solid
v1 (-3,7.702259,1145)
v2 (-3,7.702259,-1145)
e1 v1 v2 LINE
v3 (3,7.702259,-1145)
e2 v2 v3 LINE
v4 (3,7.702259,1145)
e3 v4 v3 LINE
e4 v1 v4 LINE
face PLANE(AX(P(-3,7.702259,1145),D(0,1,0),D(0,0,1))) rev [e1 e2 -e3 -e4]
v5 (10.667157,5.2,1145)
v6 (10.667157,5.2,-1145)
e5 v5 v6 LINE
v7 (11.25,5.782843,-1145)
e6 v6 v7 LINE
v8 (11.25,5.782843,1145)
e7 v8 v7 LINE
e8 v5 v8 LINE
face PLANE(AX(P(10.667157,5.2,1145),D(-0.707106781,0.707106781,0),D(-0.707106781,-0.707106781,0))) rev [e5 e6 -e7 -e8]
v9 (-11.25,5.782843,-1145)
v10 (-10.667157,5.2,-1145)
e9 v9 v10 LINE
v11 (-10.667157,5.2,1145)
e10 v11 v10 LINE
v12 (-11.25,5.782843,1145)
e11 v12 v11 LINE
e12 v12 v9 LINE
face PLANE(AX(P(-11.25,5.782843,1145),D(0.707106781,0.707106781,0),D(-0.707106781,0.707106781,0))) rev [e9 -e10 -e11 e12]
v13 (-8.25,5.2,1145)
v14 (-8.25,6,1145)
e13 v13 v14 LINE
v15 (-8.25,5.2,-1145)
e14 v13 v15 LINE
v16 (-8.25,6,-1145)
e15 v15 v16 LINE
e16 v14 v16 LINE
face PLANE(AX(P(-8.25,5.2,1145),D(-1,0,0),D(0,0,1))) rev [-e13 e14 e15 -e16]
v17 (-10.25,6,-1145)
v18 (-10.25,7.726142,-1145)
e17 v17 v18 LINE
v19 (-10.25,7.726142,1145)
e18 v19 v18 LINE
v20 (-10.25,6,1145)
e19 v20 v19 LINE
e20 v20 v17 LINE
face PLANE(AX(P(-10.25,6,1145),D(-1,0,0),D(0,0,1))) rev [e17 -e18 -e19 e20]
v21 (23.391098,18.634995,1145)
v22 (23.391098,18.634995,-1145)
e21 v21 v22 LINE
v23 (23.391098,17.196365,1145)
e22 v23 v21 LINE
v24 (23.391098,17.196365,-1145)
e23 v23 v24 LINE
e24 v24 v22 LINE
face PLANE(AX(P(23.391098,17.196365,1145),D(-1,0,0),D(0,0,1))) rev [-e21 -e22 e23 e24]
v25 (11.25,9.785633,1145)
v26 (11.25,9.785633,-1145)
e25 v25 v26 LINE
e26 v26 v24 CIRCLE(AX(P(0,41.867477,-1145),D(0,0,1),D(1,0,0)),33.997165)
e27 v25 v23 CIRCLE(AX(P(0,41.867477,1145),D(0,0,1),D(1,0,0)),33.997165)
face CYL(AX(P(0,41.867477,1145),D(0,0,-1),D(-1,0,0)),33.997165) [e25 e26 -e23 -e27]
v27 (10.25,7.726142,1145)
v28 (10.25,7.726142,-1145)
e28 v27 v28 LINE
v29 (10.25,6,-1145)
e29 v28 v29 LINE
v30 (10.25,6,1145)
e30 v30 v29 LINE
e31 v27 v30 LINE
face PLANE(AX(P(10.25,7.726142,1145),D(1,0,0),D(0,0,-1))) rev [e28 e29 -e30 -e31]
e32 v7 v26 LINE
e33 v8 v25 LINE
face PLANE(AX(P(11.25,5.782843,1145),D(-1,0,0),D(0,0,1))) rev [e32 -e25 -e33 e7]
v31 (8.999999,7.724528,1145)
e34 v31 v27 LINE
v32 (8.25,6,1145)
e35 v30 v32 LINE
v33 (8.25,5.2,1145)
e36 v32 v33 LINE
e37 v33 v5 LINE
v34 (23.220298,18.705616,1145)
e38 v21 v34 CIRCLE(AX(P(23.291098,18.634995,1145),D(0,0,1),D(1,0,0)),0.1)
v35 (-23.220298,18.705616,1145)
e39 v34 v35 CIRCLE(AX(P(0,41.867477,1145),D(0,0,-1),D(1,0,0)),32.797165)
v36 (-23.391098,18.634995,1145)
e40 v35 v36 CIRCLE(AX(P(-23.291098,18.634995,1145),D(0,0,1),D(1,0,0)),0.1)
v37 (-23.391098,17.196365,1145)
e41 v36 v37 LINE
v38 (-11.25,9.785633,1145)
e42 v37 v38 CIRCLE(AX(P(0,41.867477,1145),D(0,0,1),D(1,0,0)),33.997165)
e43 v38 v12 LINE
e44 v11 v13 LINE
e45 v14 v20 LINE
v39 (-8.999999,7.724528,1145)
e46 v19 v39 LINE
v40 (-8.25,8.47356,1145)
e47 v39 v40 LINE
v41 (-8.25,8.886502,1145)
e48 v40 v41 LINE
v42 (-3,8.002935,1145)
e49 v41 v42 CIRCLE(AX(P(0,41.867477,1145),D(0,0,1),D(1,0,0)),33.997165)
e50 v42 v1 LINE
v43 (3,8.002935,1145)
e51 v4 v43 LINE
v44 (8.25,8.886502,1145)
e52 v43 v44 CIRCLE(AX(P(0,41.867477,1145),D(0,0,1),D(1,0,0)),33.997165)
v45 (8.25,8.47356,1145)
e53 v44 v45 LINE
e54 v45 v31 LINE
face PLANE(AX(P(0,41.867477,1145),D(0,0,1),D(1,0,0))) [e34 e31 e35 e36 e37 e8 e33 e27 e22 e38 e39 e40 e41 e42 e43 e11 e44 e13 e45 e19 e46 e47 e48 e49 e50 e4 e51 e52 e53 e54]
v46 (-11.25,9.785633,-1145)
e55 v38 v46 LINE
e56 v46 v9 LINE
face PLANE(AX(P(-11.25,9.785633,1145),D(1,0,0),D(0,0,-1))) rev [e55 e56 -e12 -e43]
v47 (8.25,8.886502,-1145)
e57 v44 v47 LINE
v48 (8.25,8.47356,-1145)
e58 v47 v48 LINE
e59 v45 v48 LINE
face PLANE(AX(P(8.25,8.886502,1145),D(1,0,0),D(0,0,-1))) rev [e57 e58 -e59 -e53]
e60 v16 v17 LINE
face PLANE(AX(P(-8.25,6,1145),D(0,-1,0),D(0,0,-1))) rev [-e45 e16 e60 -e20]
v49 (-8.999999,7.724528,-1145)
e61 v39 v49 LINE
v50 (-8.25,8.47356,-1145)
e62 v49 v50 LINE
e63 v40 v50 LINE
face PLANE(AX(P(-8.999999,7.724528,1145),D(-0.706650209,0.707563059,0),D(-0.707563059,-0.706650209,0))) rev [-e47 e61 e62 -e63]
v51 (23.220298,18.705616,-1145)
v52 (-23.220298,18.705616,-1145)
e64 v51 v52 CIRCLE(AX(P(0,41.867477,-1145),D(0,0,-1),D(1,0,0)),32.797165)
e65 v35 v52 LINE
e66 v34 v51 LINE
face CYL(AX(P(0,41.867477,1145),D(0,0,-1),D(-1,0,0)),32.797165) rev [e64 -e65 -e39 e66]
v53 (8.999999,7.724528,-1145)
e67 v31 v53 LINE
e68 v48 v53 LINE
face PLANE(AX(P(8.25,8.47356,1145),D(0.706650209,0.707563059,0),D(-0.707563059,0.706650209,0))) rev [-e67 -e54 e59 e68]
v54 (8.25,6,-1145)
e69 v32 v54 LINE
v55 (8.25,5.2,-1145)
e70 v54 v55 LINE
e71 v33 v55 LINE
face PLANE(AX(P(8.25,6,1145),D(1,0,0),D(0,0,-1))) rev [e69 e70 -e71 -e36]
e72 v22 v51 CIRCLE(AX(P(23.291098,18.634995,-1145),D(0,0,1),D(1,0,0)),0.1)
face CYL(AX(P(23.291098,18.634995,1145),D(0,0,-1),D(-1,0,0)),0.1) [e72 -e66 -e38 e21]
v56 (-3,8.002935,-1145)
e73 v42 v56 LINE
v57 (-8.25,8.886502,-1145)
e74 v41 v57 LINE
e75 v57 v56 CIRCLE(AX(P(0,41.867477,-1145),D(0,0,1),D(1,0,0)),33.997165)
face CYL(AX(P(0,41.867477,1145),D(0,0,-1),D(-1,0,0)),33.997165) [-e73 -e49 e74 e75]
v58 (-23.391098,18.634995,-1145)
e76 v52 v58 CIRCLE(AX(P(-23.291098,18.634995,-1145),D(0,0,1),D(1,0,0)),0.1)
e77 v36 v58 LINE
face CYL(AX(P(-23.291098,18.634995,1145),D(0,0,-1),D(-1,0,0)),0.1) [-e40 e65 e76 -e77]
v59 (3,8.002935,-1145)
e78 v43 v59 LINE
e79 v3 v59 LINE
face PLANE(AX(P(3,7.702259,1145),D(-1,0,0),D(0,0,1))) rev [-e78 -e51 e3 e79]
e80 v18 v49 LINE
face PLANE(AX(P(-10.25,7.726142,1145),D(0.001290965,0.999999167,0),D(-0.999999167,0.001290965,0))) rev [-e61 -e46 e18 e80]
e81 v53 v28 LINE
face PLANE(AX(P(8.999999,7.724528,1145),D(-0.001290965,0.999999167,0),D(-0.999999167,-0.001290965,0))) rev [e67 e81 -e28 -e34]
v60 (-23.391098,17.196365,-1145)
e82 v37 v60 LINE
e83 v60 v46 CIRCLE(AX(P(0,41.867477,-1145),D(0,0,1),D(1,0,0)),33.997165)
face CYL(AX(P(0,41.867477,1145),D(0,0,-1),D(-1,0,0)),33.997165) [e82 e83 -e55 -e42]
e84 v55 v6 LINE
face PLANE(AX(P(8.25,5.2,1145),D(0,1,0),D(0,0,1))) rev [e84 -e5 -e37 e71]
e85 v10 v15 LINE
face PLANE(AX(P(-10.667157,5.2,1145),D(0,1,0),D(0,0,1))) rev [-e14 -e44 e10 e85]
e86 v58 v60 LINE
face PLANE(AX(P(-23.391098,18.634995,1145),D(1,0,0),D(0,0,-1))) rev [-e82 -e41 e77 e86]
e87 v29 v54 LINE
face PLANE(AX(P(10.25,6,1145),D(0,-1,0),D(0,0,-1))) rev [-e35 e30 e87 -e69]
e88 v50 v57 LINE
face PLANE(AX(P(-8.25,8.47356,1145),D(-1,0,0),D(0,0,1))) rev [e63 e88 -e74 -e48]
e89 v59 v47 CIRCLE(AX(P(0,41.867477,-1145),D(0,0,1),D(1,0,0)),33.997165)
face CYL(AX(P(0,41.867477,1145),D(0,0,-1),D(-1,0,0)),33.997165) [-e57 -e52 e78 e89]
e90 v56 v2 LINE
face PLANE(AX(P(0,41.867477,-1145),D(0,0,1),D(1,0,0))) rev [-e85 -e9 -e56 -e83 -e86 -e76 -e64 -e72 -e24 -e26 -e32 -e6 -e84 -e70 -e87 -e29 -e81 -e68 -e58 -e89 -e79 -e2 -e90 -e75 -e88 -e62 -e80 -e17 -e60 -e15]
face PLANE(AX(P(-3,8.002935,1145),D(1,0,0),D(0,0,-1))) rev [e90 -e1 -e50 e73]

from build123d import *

# Parameters (mm, degrees)
EXTRUDE_1_DEPTH = 1145


with BuildPart() as part:
    # 草图2 → 凸台-拉伸1 (new, symmetric)
    with BuildSketch(Plane.XY):
        with BuildLine():
            Line((-11.25, 5.782842712), (-10.667157288, 5.199999999))
            Line((-10.667157288, 5.199999999), (-8.25, 5.199999999))
            Line((-8.25, 5.199999999), (-8.25, 6))
            Line((-8.25, 6), (-10.25, 6))
            Line((-10.25, 6), (-10.25, 7.726142057))
            Line((-10.25, 7.726142057), (-8.999999375, 7.724528349))
            Line((-8.999999375, 7.724528349), (-8.25, 8.473560125))
            Line((-8.25, 8.473560125), (-8.25, 8.88650173))
            ThreePointArc((-8.25, 8.88650173), (-5.642322013, 8.341793831), (-3, 8.002934636))
            Line((-3, 8.002934636), (-3, 7.70225919))
            Line((-3, 7.70225919), (3, 7.70225919))
            Line((3, 7.70225919), (3, 8.002934636))
            ThreePointArc((3, 8.002934636), (5.642322013, 8.341793831), (8.25, 8.88650173))
            Line((8.25, 8.88650173), (8.25, 8.473560125))
            Line((8.25, 8.473560125), (8.999999375, 7.724528349))
            Line((8.999999375, 7.724528349), (10.25, 7.726142057))
            Line((10.25, 7.726142057), (10.25, 6))
            Line((10.25, 6), (8.25, 6))
            Line((8.25, 6), (8.25, 5.2))
            Line((8.25, 5.2), (10.667157288, 5.2))
            Line((10.667157288, 5.2), (11.25, 5.782842712))
            Line((11.25, 5.782842712), (11.25, 9.785632758))
            ThreePointArc((11.25, 9.785632758), (17.712457567, 12.84892987), (23.391097866, 17.196364903))
            Line((23.391097866, 17.196364903), (23.391097866, 18.63499481))
            ThreePointArc((23.391097866, 18.63499481), (23.329308001, 18.727406852), (23.220298155, 18.705616343))
            ThreePointArc((23.220298155, 18.705616343), (0, 9.070311977), (-23.220298155, 18.705616342))
            ThreePointArc((-23.220298155, 18.705616342), (-23.329308002, 18.727406852), (-23.391097866, 18.634994809))
            Line((-23.391097866, 18.634994809), (-23.391097866, 17.196364902))
            ThreePointArc((-23.391097866, 17.196364902), (-17.712457568, 12.84892987), (-11.25, 9.785632758))
            Line((-11.25, 9.785632758), (-11.25, 5.782842712))
        make_face()
    extrude(amount=EXTRUDE_1_DEPTH, both=True)


solid = part.part
